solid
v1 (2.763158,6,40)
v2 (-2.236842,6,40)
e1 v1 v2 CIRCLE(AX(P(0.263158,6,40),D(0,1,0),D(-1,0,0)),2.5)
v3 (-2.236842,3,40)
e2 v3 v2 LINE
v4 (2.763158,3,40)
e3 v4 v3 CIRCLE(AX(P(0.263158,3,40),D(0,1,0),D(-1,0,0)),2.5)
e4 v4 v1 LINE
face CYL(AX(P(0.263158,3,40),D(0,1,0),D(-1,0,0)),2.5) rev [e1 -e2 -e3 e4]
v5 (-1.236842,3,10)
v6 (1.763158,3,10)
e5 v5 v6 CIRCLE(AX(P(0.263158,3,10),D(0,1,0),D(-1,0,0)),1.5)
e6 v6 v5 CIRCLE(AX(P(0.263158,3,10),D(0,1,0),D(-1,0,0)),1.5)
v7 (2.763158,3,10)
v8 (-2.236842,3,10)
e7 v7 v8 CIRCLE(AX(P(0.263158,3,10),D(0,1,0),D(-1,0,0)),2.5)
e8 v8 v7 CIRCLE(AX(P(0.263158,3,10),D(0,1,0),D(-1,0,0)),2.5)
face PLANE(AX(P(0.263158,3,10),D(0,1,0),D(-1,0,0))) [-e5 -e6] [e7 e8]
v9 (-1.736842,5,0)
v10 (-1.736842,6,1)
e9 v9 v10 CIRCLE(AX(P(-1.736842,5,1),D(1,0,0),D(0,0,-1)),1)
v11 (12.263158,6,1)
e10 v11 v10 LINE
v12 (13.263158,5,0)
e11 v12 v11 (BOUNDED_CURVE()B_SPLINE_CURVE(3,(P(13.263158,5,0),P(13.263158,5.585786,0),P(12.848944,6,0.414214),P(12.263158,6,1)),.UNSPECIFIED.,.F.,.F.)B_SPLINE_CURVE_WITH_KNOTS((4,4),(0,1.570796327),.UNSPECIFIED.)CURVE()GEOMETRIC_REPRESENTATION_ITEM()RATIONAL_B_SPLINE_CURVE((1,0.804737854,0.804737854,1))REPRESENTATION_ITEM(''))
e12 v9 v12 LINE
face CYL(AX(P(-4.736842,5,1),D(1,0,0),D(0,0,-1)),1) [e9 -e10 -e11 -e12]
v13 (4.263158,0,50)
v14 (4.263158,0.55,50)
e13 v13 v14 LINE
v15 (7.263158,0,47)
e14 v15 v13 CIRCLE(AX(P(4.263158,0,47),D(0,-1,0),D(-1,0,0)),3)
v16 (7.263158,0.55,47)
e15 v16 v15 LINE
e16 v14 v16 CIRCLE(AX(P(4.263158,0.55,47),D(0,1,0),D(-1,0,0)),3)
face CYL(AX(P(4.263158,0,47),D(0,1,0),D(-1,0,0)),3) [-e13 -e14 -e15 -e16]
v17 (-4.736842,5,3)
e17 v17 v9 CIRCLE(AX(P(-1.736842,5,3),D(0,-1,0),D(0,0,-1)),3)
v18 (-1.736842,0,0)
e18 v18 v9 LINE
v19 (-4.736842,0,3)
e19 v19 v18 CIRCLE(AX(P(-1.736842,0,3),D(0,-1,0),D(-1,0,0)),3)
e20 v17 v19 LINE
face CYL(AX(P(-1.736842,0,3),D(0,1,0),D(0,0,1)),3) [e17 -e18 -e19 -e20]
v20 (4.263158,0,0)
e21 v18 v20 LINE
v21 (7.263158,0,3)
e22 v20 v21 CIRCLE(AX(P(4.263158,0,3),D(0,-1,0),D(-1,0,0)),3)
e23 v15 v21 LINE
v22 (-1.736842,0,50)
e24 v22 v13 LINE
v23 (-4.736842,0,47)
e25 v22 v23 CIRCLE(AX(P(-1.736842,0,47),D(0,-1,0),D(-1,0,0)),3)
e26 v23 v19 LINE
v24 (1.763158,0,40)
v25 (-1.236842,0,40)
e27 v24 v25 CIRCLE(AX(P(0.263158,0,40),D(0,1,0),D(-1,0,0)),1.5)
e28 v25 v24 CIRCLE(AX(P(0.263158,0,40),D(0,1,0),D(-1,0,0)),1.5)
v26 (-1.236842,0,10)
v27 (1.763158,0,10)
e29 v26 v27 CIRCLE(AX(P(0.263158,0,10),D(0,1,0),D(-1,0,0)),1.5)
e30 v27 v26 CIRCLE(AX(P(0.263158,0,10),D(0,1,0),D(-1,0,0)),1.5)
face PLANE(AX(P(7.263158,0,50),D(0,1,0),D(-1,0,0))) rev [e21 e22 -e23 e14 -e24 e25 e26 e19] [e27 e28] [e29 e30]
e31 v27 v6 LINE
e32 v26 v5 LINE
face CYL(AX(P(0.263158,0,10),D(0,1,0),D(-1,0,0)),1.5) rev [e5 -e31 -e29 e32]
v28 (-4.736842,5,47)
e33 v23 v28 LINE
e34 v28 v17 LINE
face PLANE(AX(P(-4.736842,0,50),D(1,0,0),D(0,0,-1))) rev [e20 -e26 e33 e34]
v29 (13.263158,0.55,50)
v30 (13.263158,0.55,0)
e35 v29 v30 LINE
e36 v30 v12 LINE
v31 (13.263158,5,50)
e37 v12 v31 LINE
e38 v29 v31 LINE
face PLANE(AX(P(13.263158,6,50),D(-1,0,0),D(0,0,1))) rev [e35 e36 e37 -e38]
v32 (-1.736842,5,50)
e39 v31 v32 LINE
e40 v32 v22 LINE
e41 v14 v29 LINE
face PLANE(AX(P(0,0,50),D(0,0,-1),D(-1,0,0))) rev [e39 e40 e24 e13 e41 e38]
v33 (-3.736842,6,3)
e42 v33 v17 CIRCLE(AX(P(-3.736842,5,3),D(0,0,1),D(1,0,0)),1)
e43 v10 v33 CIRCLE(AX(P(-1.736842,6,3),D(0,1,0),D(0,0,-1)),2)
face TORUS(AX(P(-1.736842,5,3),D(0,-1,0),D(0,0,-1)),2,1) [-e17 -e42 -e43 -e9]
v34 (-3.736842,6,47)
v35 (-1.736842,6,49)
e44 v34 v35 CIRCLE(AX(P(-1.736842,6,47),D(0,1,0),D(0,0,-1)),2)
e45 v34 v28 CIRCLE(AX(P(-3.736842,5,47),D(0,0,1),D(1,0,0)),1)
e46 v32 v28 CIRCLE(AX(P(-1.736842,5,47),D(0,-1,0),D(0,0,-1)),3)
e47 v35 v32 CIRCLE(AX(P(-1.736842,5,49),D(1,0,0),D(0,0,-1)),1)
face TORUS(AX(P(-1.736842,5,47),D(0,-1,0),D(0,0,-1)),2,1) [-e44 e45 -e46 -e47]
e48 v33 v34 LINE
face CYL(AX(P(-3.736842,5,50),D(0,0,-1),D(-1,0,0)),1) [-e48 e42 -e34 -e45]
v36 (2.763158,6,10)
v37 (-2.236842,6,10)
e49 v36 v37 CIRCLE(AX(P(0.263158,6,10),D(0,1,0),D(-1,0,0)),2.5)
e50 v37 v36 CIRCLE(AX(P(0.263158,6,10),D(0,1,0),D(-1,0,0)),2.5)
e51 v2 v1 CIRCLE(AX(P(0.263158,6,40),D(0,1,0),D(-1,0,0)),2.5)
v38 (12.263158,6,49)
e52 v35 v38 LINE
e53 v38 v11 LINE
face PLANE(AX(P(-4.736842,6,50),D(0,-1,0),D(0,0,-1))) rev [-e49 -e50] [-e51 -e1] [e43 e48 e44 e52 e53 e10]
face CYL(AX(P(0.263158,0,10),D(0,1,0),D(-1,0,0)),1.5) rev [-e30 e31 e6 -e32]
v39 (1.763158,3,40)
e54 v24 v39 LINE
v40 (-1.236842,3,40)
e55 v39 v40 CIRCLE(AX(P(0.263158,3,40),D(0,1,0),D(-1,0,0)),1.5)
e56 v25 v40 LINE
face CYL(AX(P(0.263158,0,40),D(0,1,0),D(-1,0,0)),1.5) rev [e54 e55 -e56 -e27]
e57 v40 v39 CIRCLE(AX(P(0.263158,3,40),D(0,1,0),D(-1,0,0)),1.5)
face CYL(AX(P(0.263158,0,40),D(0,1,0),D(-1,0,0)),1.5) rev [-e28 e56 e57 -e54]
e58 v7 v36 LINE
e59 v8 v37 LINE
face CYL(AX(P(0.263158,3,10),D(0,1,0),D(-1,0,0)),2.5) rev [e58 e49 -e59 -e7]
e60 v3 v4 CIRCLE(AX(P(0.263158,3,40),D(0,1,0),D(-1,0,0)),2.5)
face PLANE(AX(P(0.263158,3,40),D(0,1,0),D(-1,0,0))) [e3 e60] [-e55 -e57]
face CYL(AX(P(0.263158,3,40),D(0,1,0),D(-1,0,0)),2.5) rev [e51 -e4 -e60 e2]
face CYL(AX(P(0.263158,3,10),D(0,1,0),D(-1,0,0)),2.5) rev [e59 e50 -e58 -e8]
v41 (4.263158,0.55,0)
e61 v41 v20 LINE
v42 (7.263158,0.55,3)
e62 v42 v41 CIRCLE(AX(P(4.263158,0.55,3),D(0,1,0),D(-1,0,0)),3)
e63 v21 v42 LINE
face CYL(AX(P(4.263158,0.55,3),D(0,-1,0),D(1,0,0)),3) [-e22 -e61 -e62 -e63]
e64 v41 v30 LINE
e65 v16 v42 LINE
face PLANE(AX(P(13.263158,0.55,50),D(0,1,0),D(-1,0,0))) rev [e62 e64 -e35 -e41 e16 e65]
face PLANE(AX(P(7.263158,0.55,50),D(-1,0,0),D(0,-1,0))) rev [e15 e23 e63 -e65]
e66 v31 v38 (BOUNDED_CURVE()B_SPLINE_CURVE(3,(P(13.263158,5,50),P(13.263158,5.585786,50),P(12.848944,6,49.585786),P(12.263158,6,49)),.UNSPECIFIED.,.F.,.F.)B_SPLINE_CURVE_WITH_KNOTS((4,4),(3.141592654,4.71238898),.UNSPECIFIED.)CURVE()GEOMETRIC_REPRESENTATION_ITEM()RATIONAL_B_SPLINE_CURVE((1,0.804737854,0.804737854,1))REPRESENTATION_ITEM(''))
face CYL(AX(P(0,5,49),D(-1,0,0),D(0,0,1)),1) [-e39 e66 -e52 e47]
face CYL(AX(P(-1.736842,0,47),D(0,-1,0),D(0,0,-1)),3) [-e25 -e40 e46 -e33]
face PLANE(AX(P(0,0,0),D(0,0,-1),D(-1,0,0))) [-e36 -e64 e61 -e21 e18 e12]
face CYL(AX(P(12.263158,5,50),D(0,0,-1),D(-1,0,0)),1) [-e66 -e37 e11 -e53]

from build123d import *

# Parameters (mm, degrees)
BOSS_EXTRUDE1_DEPTH = 50
FILLET1_R           = 3
SKETCH3_R           = 2.5
CUT_EXTRUDE1_DEPTH  = 3
SKETCH4_R           = 1.5
CUT_EXTRUDE2_DEPTH  = 52.816130281
SKETCH5_R           = 1.5
CUT_EXTRUDE3_DEPTH  = 52.816130281
FILLET5_R           = 3
FILLET6_R           = 3
FILLET7_R           = 1


with BuildPart() as part:
    # Sketch1 → Boss-Extrude1 (new body)
    with BuildSketch(Plane.XY):
        Polygon((-4.736842105, 0), (-4.736842105, 6), (13.263157895, 6), (13.263157895, 0.55), (7.263157895, 0.55), (7.263157895, 0), align=None)
    extrude(amount=BOSS_EXTRUDE1_DEPTH)

    # Fillet1
    fillet1_edges = [part.edges().sort_by_distance(p)[0] for p in [
        (7.263157895, 0.275, 50),
    ]]
    fillet(fillet1_edges, radius=FILLET1_R)

    # Sketch3 → Cut-Extrude1 (cut)
    with BuildSketch(Plane(origin=(0, 6, 0), x_dir=(1, 0, 0), z_dir=(0, 1, 0))):
        with Locations(Location((0.263157895, -10, 0), (0, 0, 180))):
            Circle(SKETCH3_R)
        with Locations(Location((0.263157895, -40, 0), (0, 0, 180))):
            Circle(SKETCH3_R)
    extrude(amount=-CUT_EXTRUDE1_DEPTH, mode=Mode.SUBTRACT)

    # Sketch4 → Cut-Extrude2 (cut, through all)
    with BuildSketch(Plane(origin=(0, 3, 0), x_dir=(1, 0, 0), z_dir=(0, 1, 0))):
        with Locations(Location((0.263157895, -40, 0), (0, 0, 180))):
            Circle(SKETCH4_R)
    extrude(amount=-CUT_EXTRUDE2_DEPTH, mode=Mode.SUBTRACT)

    # Sketch5 → Cut-Extrude3 (cut, through all)
    with BuildSketch(Plane(origin=(0, 3, 0), x_dir=(1, 0, 0), z_dir=(0, 1, 0))):
        with Locations(Location((0.263157895, -10, 0), (0, 0, 180))):
            Circle(SKETCH5_R)
    extrude(amount=-CUT_EXTRUDE3_DEPTH, mode=Mode.SUBTRACT)

    # Fillet5
    fillet5_edges = [part.edges().sort_by_distance(p)[0] for p in [
        (7.263157895, 0.275, 0),
    ]]
    fillet(fillet5_edges, radius=FILLET5_R)

    # Fillet6
    fillet6_edges = [part.edges().sort_by_distance(p)[0] for p in [
        (-4.736842105, 3, 50),
        (-4.736842105, 3, 0),
    ]]
    fillet(fillet6_edges, radius=FILLET6_R)

    # Fillet7
    fillet7_edges = [part.edges().sort_by_distance(p)[0] for p in [
        (13.263157895, 6, 25),
        (5.763157895, 6, 50),
        (-4.736842105, 6, 25),
        (-3.858162449, 6, 49.121320344),
        (-3.858162449, 6, 0.878679656),
        (5.763157895, 6, 0),
    ]]
    fillet(fillet7_edges, radius=FILLET7_R)


solid = part.part
